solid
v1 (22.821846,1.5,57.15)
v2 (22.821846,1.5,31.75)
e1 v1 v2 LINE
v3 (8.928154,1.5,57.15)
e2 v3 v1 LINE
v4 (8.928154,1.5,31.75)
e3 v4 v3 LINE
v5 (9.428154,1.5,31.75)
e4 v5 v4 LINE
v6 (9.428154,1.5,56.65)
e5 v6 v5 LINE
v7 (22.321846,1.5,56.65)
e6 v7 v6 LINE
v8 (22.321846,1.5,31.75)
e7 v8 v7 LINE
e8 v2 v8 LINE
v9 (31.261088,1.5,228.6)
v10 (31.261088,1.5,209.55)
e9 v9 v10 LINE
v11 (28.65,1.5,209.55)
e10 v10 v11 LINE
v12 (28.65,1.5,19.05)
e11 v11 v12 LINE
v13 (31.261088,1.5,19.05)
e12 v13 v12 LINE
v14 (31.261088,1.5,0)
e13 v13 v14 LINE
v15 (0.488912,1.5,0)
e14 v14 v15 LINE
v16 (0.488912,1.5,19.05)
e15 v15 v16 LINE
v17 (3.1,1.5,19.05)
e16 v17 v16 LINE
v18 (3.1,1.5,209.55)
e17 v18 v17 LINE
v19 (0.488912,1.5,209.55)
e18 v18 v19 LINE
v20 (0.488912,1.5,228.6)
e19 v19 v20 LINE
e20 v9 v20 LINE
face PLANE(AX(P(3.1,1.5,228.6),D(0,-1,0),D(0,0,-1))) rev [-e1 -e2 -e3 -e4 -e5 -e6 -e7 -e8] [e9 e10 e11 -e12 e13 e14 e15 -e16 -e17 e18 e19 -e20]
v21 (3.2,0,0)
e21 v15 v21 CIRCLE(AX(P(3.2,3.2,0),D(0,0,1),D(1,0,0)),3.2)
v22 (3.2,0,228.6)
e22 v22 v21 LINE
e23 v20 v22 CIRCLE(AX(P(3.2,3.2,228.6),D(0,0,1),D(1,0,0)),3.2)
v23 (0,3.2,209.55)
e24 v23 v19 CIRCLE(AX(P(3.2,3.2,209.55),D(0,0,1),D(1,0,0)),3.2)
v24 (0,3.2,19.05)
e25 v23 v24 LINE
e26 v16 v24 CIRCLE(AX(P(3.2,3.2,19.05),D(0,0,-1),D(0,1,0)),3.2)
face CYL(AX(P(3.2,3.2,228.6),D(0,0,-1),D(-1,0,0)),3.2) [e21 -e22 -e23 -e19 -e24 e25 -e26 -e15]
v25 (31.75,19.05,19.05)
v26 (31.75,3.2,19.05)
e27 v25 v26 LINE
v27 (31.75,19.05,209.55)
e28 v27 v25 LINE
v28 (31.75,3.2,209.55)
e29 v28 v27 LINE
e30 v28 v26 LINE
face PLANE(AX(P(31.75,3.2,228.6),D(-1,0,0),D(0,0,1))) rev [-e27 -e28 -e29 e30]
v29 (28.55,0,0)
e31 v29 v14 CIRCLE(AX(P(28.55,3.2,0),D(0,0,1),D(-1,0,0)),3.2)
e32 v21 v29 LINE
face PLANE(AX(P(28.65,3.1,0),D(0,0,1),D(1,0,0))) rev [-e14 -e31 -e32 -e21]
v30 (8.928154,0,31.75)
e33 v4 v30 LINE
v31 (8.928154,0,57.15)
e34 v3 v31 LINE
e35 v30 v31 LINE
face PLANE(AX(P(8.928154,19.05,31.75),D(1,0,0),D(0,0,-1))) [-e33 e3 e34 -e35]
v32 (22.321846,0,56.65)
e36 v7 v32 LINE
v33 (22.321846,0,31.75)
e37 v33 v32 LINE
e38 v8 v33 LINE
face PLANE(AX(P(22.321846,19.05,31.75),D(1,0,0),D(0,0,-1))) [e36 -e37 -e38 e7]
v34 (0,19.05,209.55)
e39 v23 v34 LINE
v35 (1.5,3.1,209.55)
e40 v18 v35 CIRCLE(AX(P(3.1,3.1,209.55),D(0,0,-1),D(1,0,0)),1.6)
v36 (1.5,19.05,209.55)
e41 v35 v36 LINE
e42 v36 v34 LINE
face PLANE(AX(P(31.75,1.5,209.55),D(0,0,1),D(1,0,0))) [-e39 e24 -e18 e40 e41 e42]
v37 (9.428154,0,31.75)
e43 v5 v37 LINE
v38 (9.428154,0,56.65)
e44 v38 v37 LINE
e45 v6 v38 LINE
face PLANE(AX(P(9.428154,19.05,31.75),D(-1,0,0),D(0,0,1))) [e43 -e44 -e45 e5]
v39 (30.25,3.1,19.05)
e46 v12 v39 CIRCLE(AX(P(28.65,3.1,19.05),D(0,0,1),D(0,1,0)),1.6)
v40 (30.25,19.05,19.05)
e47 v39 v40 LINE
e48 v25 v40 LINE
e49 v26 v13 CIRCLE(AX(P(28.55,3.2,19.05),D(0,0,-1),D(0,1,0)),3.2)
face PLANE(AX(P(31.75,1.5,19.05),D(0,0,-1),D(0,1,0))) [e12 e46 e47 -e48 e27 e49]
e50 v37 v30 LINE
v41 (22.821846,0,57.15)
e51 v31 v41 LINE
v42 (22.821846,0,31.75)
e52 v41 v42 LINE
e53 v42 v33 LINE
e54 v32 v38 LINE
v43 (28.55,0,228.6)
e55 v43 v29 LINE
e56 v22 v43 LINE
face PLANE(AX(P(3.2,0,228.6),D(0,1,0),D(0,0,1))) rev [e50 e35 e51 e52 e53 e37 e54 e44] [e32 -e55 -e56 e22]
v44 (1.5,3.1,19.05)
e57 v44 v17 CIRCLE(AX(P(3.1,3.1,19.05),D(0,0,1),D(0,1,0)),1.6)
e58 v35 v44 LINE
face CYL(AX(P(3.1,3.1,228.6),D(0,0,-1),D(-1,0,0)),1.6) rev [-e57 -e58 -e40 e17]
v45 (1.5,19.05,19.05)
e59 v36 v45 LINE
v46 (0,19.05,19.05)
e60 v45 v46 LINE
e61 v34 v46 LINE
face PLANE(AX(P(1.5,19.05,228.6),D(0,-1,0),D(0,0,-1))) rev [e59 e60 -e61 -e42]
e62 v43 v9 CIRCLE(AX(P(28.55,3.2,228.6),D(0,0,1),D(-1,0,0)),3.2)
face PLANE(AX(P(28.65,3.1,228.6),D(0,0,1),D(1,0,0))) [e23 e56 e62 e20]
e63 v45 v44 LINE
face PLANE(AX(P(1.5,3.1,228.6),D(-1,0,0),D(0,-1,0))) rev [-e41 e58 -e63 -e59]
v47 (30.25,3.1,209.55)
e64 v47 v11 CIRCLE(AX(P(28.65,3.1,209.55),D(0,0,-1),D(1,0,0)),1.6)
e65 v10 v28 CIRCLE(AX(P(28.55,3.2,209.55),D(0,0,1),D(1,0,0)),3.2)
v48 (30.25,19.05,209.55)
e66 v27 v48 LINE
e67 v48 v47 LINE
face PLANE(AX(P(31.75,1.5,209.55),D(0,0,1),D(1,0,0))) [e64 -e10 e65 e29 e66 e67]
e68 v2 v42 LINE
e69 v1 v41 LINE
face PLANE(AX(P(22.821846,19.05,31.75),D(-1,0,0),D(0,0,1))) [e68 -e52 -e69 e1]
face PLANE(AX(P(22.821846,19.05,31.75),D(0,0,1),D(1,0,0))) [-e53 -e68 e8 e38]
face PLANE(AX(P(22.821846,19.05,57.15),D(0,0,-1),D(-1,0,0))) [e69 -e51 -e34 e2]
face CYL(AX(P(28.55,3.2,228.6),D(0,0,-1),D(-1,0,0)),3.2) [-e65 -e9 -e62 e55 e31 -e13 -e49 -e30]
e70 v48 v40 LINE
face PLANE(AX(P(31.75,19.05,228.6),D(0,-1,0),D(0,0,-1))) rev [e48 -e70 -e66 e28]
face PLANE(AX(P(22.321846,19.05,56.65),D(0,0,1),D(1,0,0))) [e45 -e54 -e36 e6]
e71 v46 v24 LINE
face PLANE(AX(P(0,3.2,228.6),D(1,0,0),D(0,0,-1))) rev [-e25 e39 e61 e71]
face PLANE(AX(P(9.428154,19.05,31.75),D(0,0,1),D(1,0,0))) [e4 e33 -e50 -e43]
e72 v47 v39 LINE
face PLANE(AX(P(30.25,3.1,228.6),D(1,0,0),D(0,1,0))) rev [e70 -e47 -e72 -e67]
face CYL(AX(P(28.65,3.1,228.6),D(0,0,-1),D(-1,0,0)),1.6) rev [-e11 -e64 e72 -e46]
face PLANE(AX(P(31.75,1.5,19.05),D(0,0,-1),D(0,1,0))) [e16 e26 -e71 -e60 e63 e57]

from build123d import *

# Parameters (mm, degrees)
BOSS_EXTRUDE1_DEPTH = 228.6
SKETCH2_W           = 19.05
SKETCH2_H           = 17.55
CUT_EXTRUDE1_DEPTH  = 232.579198116
CUT_EXTRUDE2_DEPTH  = 232.579198116


with BuildPart() as part:
    # Sketch1 → Boss-Extrude1 (new body)
    with BuildSketch(Plane.XY):
        with BuildLine():
            Line((30.25, 3.1), (30.25, 19.05))
            Line((30.25, 19.05), (31.75, 19.05))
            Line((31.75, 19.05), (31.75, 3.2))
            ThreePointArc((31.75, 3.2), (30.8127417, 0.9372583), (28.55, 0))
            Line((28.55, 0), (3.2, 0))
            ThreePointArc((3.2, 0), (0.9372583, 0.9372583), (0, 3.2))
            Line((0, 3.2), (0, 19.05))
            Line((0, 19.05), (1.5, 19.05))
            Line((1.5, 19.05), (1.5, 3.1))
            ThreePointArc((1.5, 3.1), (1.96862915, 1.96862915), (3.1, 1.5))
            Line((3.1, 1.5), (28.65, 1.5))
            ThreePointArc((28.65, 1.5), (29.78137085, 1.96862915), (30.25, 3.1))
        make_face()
    extrude(amount=BOSS_EXTRUDE1_DEPTH)

    # Sketch2 → Cut-Extrude1 (cut, through all)
    with BuildSketch(Plane(origin=(0, 0, 0), x_dir=(0, 0, -1), z_dir=(1, 0, 0))):
        with Locations((-9.525, 10.275)):
            Rectangle(SKETCH2_W, SKETCH2_H)
        with Locations((-219.075, 10.275)):
            Rectangle(SKETCH2_W, SKETCH2_H)
    extrude(amount=CUT_EXTRUDE1_DEPTH, mode=Mode.SUBTRACT)

    # Sketch3 → Cut-Extrude2 (cut, through all)
    with BuildSketch(Plane(origin=(0, 0, 0), x_dir=(1, 0, 0), z_dir=(0, 1, 0))):
        Polygon((22.821846385, -57.15), (8.928153615, -57.15), (8.928153615, -31.75), (9.428153615, -31.75), (9.428153615, -56.65), (22.321846385, -56.65), (22.321846385, -31.75), (22.821846385, -31.75), align=None)
    extrude(amount=CUT_EXTRUDE2_DEPTH, mode=Mode.SUBTRACT)


solid = part.part
